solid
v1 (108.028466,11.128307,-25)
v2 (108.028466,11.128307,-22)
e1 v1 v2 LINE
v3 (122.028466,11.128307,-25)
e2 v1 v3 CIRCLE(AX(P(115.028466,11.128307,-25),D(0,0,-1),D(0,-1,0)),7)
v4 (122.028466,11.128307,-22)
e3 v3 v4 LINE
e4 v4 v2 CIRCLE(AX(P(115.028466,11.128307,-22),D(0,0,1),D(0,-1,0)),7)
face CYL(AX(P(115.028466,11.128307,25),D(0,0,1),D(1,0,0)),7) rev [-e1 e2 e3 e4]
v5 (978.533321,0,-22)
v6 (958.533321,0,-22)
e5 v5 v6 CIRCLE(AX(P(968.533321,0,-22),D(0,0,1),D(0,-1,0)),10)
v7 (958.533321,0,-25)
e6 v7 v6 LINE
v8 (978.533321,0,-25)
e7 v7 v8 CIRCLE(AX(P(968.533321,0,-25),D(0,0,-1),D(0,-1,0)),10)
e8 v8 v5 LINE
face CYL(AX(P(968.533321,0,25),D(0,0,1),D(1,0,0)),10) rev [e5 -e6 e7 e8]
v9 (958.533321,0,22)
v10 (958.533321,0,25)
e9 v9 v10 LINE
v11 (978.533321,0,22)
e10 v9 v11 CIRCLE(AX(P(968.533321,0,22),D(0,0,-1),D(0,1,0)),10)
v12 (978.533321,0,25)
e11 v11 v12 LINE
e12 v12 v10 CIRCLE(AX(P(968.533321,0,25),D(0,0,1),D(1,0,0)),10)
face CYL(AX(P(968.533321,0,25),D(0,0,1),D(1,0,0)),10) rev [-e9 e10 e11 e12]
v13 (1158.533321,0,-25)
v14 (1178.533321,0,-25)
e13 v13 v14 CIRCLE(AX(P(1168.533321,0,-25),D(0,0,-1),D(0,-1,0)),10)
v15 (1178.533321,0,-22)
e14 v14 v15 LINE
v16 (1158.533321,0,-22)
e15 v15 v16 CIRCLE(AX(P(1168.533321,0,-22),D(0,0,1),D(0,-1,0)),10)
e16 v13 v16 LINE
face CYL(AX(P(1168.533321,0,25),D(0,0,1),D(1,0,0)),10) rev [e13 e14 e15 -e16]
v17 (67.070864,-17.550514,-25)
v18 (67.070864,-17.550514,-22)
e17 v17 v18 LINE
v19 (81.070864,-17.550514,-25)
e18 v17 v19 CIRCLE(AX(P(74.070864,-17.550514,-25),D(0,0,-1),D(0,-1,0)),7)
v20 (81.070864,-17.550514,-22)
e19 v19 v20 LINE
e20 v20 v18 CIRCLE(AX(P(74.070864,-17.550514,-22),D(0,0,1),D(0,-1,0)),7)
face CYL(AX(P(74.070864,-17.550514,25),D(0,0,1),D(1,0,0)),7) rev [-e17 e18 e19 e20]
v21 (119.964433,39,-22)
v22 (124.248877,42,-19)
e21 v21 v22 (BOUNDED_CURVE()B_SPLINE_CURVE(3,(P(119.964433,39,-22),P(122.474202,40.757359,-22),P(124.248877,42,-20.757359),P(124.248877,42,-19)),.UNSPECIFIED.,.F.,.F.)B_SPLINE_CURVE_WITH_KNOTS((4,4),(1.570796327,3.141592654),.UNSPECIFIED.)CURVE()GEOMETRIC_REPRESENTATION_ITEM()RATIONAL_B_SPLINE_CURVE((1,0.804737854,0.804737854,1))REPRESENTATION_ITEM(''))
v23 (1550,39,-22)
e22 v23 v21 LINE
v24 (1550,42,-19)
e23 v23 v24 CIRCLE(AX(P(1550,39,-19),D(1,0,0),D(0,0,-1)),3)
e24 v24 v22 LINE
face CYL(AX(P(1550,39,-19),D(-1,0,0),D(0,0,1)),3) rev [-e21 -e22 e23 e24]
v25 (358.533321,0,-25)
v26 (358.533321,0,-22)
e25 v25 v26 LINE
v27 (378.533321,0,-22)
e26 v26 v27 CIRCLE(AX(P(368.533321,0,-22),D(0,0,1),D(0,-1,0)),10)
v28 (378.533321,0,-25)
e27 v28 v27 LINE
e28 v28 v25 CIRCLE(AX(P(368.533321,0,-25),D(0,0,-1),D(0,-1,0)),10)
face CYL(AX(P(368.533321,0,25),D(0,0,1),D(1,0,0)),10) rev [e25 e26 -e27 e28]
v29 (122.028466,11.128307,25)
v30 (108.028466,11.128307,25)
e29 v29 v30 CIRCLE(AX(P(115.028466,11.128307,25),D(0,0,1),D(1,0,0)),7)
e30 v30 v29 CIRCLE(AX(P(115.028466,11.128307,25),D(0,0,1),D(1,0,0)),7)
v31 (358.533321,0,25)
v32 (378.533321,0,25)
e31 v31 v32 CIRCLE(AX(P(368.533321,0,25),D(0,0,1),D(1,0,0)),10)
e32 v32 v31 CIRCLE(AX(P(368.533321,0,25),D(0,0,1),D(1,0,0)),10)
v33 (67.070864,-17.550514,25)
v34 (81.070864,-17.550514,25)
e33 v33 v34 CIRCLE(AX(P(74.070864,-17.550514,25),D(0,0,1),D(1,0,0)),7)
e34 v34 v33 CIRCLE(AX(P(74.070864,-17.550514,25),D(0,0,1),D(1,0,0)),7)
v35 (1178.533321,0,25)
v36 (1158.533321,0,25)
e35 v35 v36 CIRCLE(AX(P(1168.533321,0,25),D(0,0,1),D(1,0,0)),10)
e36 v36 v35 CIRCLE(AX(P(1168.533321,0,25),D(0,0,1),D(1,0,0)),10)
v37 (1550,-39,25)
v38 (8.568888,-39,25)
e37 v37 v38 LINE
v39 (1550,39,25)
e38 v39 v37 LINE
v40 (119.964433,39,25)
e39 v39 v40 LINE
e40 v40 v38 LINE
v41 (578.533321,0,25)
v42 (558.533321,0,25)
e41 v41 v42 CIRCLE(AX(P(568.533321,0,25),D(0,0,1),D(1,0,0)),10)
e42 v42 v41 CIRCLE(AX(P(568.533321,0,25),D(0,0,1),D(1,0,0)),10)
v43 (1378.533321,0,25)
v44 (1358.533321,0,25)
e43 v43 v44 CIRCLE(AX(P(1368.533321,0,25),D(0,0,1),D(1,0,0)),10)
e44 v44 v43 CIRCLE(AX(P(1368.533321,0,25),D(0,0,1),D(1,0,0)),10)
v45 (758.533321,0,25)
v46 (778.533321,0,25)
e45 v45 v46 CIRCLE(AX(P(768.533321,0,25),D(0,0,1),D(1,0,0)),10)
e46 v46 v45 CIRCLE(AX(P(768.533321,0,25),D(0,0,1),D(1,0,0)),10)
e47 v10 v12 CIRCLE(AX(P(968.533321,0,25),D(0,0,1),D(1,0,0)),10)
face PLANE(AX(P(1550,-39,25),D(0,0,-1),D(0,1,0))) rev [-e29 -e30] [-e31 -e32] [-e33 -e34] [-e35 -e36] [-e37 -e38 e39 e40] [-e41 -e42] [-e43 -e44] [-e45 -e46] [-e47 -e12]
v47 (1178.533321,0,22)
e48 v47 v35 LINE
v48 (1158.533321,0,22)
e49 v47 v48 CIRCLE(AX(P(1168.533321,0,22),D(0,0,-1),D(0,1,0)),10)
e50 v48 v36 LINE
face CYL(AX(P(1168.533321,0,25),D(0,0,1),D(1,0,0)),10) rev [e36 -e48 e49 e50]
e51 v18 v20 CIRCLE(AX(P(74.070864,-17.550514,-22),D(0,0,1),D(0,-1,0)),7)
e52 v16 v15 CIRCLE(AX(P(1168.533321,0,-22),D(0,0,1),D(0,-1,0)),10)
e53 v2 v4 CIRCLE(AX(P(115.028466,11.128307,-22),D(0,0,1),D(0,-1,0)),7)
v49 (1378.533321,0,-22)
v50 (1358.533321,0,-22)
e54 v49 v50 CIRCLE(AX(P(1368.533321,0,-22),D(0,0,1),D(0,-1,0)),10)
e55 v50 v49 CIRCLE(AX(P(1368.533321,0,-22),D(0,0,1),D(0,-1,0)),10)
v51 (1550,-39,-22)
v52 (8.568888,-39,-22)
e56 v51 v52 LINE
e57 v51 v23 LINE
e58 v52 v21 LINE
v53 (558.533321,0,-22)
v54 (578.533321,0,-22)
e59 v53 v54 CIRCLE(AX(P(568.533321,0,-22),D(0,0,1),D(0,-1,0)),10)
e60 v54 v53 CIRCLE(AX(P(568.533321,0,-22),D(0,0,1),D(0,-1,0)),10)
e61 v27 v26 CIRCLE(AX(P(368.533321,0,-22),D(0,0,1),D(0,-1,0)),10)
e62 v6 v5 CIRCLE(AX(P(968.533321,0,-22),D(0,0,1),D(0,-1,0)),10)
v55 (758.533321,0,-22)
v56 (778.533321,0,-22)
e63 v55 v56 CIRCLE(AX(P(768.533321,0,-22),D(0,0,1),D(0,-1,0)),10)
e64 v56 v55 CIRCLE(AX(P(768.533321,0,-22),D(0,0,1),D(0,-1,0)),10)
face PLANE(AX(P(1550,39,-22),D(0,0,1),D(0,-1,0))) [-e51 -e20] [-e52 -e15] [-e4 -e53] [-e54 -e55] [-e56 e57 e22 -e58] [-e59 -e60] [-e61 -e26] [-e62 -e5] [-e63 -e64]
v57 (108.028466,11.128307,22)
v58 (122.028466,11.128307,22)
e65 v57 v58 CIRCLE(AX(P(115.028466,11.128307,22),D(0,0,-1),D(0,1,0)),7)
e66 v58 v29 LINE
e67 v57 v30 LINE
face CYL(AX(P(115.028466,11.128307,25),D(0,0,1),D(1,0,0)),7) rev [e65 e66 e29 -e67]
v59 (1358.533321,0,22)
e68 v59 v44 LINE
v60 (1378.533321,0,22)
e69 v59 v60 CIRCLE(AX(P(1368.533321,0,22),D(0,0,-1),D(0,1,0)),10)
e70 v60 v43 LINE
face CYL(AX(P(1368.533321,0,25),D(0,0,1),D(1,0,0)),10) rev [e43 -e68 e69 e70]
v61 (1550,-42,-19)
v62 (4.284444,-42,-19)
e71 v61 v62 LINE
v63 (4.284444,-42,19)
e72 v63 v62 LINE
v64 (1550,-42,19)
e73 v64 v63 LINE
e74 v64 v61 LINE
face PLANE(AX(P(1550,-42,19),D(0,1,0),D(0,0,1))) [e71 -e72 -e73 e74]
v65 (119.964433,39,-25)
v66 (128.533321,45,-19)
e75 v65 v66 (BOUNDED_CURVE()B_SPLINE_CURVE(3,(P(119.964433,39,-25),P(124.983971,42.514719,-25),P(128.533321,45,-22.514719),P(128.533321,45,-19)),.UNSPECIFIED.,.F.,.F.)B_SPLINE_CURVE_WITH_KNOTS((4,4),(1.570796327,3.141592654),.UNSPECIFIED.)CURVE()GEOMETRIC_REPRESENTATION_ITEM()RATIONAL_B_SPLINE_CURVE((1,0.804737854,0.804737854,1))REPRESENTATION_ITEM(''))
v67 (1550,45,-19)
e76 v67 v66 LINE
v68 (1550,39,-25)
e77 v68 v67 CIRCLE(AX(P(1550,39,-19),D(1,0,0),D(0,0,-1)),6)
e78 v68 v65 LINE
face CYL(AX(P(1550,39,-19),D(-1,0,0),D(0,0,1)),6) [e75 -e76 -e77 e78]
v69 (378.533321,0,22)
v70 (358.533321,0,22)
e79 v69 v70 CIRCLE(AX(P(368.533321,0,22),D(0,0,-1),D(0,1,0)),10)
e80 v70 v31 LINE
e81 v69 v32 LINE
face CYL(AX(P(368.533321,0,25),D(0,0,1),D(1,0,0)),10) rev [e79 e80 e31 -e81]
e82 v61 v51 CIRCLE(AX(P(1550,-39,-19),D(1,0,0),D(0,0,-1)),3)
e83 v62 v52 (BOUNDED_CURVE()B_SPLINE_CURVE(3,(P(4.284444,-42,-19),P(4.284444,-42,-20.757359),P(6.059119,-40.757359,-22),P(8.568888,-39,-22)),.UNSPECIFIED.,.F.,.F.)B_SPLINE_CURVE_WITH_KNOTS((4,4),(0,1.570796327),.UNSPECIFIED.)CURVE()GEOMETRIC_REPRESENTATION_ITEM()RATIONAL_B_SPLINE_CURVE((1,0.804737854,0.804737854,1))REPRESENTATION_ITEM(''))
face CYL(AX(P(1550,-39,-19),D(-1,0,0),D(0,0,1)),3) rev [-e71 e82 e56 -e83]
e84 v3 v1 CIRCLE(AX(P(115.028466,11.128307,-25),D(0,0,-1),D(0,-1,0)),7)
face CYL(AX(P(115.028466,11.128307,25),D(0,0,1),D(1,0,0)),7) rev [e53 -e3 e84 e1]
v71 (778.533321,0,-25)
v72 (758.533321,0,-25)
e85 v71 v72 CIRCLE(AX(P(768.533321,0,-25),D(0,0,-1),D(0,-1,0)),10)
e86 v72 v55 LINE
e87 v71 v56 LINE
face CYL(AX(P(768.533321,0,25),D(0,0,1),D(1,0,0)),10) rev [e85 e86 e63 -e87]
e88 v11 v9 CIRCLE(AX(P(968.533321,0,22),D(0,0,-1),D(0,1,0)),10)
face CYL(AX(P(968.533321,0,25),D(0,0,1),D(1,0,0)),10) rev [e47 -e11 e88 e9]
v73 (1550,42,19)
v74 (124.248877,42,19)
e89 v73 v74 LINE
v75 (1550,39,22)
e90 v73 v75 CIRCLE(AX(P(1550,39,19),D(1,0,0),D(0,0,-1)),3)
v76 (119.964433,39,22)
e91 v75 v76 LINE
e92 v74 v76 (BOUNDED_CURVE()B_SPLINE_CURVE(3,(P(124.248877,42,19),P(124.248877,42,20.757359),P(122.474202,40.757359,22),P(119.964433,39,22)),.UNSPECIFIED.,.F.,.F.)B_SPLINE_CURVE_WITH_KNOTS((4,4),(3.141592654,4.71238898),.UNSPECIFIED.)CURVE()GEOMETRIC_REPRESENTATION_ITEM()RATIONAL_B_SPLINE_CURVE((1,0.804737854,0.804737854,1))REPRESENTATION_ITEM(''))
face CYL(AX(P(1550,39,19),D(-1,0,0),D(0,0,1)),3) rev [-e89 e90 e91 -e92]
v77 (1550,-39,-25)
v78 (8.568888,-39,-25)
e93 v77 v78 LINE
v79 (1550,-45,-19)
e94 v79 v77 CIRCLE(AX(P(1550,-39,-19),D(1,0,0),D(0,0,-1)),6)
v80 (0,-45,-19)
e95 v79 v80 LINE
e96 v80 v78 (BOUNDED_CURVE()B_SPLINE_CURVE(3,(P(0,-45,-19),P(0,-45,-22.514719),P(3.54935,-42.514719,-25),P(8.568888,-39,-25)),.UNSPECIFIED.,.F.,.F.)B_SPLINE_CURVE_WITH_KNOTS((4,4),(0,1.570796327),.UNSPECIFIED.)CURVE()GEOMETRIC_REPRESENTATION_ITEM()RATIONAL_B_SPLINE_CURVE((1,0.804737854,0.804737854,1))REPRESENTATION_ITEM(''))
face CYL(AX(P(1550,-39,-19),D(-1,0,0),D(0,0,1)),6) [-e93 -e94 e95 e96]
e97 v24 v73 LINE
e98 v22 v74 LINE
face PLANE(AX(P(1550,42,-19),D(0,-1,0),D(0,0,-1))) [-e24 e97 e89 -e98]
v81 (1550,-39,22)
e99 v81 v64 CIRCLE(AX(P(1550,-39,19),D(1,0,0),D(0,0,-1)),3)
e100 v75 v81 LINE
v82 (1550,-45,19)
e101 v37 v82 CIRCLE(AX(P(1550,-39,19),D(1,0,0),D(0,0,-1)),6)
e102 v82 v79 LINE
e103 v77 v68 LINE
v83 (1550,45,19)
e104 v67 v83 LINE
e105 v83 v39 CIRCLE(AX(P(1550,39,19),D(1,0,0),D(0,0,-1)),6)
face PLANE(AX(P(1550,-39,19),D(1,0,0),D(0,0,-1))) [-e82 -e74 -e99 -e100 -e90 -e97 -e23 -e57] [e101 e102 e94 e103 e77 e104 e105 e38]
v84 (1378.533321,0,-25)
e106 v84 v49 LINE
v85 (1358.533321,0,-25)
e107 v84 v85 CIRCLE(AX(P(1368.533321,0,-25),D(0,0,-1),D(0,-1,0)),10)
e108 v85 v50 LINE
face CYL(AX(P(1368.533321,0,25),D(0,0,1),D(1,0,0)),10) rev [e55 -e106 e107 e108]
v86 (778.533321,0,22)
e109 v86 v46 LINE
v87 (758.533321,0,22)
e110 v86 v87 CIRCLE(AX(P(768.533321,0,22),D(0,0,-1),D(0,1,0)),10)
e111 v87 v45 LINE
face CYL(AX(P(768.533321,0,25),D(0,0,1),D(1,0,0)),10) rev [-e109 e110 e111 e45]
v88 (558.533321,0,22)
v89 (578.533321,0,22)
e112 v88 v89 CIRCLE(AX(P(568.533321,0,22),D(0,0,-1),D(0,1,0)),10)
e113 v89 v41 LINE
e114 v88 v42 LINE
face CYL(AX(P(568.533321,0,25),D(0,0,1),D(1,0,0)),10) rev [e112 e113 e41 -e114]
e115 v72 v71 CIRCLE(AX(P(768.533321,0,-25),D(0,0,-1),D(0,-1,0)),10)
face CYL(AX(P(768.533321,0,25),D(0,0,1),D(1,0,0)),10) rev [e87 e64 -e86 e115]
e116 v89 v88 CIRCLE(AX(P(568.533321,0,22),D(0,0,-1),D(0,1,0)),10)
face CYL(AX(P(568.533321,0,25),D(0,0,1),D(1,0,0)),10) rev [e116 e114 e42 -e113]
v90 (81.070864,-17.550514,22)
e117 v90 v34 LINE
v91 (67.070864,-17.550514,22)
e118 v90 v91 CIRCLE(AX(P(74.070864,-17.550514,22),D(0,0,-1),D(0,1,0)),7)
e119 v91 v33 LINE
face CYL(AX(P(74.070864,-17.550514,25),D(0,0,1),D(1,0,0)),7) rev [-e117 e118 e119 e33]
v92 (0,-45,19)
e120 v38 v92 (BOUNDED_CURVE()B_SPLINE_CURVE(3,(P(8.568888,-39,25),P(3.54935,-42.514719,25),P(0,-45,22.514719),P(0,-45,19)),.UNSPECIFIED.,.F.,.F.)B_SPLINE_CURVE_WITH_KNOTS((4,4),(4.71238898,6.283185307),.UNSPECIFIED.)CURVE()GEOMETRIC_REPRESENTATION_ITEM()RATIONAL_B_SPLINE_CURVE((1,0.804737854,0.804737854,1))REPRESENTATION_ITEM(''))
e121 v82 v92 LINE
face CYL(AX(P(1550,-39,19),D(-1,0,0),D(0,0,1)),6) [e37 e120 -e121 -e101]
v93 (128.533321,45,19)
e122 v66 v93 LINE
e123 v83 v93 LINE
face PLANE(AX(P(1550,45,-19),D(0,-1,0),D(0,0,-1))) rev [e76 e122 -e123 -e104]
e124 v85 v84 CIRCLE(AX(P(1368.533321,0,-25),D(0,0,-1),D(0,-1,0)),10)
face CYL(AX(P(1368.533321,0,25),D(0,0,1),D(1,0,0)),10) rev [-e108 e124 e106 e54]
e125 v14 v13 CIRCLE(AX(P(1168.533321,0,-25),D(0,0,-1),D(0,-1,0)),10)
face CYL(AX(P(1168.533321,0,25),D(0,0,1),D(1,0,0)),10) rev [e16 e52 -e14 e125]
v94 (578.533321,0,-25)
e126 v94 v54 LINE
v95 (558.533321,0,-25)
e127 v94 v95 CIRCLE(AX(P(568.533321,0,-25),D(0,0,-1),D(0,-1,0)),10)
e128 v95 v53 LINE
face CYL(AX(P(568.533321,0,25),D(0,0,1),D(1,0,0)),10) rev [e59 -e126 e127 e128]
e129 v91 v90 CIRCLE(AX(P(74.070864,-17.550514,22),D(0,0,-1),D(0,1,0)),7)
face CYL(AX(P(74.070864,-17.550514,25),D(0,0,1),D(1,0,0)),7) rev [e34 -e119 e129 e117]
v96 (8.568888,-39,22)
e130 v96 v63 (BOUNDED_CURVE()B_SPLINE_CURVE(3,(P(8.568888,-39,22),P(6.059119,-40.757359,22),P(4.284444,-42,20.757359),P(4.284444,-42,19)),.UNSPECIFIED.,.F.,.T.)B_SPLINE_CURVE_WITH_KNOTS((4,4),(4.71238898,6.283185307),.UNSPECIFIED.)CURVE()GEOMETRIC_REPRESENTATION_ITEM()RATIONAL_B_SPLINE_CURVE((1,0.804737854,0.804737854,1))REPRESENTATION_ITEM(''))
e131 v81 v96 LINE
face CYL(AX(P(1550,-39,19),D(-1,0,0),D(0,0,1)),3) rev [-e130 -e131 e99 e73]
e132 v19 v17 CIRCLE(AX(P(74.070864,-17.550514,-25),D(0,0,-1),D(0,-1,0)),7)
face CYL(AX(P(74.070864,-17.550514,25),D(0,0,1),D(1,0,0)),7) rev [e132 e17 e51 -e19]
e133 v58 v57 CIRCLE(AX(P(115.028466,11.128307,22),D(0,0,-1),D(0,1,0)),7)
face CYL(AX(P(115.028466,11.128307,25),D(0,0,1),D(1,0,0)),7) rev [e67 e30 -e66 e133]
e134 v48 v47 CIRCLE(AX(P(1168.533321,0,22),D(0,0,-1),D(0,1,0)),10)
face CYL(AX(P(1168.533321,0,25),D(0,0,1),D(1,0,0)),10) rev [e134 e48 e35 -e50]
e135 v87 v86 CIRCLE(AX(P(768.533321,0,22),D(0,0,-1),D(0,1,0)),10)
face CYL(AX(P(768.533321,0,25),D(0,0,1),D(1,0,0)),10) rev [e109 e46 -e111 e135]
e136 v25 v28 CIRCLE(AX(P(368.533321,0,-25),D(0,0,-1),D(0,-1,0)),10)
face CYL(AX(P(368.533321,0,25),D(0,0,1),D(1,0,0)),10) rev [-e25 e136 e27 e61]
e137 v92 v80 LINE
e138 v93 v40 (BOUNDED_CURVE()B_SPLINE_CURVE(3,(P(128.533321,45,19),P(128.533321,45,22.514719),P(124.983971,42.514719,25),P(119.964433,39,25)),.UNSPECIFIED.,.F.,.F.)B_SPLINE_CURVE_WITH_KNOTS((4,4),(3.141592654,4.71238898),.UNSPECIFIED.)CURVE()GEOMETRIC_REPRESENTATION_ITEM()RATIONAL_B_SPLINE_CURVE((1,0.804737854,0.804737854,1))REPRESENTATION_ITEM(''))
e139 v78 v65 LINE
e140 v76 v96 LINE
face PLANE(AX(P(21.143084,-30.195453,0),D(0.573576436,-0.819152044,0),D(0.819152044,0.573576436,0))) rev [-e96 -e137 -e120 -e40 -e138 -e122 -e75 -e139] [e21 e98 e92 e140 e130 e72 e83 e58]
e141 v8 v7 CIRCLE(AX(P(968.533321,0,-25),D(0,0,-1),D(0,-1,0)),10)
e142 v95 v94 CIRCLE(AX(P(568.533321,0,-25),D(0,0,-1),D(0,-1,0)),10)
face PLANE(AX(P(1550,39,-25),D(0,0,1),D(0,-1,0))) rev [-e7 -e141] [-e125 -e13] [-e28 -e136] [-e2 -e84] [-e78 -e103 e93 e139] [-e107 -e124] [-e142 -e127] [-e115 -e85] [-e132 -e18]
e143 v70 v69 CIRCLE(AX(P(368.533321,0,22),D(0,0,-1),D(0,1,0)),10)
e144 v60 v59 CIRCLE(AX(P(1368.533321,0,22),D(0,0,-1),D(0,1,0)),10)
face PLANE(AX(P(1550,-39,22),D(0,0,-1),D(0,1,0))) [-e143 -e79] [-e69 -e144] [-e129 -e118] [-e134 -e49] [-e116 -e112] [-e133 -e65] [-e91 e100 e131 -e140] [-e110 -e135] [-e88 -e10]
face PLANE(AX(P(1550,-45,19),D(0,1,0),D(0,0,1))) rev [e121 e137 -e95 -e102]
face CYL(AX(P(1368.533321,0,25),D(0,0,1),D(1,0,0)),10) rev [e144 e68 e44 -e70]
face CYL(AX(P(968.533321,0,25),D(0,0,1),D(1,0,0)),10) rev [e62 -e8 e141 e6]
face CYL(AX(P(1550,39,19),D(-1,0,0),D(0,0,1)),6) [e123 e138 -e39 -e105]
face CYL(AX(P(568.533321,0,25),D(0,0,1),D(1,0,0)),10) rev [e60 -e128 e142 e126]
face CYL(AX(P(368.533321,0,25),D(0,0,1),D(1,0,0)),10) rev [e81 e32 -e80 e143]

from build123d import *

# Parameters (mm, degrees)
GB_T6728_2002_90_X_50_X_4_1_DEPTH = 1550
HOLE_WIZARD_20_0_20_1_D           = 20
PATTERN_LINEAR_1_COUNT            = 6
PATTERN_LINEAR_1_PITCH            = 200
HOLE_WIZARD_14_0_14_2_D           = 14


with BuildPart() as part:
    # Sketch11 → 冷弯空心矩管gb∕t6728-2002 90 X 50 X 4(1) (new body)
    with BuildSketch(Plane(origin=(0, 0, 0), x_dir=(0, 0, 1), z_dir=(1, 0, 0))):
        with BuildLine():
            Line((-19, -45), (19, -45))
            ThreePointArc((19, -45), (23.242640687, -43.242640687), (25, -39))
            Line((25, -39), (25, 39))
            ThreePointArc((25, 39), (23.242640687, 43.242640687), (19, 45))
            Line((19, 45), (-19, 45))
            ThreePointArc((-19, 45), (-23.242640687, 43.242640687), (-25, 39))
            Line((-25, 39), (-25, -39))
            ThreePointArc((-25, -39), (-23.242640687, -43.242640687), (-19, -45))
        make_face()
        with BuildLine():
            Line((-19, -42), (19, -42))
            ThreePointArc((19, -42), (21.121320344, -41.121320344), (22, -39))
            Line((22, -39), (22, 39))
            ThreePointArc((22, 39), (21.121320344, 41.121320344), (19, 42))
            Line((19, 42), (-19, 42))
            ThreePointArc((-19, 42), (-21.121320344, 41.121320344), (-22, 39))
            Line((-22, 39), (-22, -39))
            ThreePointArc((-22, -39), (-21.121320344, -41.121320344), (-19, -42))
        make_face(mode=Mode.SUBTRACT)
    extrude(amount=GB_T6728_2002_90_X_50_X_4_1_DEPTH)

    # Split Bodies 1
    split(bisect_by=Plane(origin=(21.143083968, -30.195453225, 0), x_dir=(-0.819152044288993, -0.5735764363510444, 0), z_dir=(0.5735764363510444, -0.819152044288993, -2.99158375078423e-15)), keep=Keep.TOP)

    # Ø20.0 (20) 直径孔1 (through all)
    with Locations(Plane.XY.offset(25)):
        with Locations((368.533320607, 0)):
            hole_wizard_20_0_20_1 = Hole(HOLE_WIZARD_20_0_20_1_D / 2)

    # 阵列(线性)1: Ø20.0 (20) 直径孔1 ×6
    with Locations(*[(i * PATTERN_LINEAR_1_PITCH, 0, 0) for i in range(1, PATTERN_LINEAR_1_COUNT)]):
        add(hole_wizard_20_0_20_1, mode=Mode.SUBTRACT)

    # Ø14.0 (14) 直径孔2 (through all)
    with Locations(Plane.XY.offset(25)):
        with Locations((115.028466248, 11.128307401), (74.070864034, -17.550514417)):
            Hole(HOLE_WIZARD_14_0_14_2_D / 2)


solid = part.part
